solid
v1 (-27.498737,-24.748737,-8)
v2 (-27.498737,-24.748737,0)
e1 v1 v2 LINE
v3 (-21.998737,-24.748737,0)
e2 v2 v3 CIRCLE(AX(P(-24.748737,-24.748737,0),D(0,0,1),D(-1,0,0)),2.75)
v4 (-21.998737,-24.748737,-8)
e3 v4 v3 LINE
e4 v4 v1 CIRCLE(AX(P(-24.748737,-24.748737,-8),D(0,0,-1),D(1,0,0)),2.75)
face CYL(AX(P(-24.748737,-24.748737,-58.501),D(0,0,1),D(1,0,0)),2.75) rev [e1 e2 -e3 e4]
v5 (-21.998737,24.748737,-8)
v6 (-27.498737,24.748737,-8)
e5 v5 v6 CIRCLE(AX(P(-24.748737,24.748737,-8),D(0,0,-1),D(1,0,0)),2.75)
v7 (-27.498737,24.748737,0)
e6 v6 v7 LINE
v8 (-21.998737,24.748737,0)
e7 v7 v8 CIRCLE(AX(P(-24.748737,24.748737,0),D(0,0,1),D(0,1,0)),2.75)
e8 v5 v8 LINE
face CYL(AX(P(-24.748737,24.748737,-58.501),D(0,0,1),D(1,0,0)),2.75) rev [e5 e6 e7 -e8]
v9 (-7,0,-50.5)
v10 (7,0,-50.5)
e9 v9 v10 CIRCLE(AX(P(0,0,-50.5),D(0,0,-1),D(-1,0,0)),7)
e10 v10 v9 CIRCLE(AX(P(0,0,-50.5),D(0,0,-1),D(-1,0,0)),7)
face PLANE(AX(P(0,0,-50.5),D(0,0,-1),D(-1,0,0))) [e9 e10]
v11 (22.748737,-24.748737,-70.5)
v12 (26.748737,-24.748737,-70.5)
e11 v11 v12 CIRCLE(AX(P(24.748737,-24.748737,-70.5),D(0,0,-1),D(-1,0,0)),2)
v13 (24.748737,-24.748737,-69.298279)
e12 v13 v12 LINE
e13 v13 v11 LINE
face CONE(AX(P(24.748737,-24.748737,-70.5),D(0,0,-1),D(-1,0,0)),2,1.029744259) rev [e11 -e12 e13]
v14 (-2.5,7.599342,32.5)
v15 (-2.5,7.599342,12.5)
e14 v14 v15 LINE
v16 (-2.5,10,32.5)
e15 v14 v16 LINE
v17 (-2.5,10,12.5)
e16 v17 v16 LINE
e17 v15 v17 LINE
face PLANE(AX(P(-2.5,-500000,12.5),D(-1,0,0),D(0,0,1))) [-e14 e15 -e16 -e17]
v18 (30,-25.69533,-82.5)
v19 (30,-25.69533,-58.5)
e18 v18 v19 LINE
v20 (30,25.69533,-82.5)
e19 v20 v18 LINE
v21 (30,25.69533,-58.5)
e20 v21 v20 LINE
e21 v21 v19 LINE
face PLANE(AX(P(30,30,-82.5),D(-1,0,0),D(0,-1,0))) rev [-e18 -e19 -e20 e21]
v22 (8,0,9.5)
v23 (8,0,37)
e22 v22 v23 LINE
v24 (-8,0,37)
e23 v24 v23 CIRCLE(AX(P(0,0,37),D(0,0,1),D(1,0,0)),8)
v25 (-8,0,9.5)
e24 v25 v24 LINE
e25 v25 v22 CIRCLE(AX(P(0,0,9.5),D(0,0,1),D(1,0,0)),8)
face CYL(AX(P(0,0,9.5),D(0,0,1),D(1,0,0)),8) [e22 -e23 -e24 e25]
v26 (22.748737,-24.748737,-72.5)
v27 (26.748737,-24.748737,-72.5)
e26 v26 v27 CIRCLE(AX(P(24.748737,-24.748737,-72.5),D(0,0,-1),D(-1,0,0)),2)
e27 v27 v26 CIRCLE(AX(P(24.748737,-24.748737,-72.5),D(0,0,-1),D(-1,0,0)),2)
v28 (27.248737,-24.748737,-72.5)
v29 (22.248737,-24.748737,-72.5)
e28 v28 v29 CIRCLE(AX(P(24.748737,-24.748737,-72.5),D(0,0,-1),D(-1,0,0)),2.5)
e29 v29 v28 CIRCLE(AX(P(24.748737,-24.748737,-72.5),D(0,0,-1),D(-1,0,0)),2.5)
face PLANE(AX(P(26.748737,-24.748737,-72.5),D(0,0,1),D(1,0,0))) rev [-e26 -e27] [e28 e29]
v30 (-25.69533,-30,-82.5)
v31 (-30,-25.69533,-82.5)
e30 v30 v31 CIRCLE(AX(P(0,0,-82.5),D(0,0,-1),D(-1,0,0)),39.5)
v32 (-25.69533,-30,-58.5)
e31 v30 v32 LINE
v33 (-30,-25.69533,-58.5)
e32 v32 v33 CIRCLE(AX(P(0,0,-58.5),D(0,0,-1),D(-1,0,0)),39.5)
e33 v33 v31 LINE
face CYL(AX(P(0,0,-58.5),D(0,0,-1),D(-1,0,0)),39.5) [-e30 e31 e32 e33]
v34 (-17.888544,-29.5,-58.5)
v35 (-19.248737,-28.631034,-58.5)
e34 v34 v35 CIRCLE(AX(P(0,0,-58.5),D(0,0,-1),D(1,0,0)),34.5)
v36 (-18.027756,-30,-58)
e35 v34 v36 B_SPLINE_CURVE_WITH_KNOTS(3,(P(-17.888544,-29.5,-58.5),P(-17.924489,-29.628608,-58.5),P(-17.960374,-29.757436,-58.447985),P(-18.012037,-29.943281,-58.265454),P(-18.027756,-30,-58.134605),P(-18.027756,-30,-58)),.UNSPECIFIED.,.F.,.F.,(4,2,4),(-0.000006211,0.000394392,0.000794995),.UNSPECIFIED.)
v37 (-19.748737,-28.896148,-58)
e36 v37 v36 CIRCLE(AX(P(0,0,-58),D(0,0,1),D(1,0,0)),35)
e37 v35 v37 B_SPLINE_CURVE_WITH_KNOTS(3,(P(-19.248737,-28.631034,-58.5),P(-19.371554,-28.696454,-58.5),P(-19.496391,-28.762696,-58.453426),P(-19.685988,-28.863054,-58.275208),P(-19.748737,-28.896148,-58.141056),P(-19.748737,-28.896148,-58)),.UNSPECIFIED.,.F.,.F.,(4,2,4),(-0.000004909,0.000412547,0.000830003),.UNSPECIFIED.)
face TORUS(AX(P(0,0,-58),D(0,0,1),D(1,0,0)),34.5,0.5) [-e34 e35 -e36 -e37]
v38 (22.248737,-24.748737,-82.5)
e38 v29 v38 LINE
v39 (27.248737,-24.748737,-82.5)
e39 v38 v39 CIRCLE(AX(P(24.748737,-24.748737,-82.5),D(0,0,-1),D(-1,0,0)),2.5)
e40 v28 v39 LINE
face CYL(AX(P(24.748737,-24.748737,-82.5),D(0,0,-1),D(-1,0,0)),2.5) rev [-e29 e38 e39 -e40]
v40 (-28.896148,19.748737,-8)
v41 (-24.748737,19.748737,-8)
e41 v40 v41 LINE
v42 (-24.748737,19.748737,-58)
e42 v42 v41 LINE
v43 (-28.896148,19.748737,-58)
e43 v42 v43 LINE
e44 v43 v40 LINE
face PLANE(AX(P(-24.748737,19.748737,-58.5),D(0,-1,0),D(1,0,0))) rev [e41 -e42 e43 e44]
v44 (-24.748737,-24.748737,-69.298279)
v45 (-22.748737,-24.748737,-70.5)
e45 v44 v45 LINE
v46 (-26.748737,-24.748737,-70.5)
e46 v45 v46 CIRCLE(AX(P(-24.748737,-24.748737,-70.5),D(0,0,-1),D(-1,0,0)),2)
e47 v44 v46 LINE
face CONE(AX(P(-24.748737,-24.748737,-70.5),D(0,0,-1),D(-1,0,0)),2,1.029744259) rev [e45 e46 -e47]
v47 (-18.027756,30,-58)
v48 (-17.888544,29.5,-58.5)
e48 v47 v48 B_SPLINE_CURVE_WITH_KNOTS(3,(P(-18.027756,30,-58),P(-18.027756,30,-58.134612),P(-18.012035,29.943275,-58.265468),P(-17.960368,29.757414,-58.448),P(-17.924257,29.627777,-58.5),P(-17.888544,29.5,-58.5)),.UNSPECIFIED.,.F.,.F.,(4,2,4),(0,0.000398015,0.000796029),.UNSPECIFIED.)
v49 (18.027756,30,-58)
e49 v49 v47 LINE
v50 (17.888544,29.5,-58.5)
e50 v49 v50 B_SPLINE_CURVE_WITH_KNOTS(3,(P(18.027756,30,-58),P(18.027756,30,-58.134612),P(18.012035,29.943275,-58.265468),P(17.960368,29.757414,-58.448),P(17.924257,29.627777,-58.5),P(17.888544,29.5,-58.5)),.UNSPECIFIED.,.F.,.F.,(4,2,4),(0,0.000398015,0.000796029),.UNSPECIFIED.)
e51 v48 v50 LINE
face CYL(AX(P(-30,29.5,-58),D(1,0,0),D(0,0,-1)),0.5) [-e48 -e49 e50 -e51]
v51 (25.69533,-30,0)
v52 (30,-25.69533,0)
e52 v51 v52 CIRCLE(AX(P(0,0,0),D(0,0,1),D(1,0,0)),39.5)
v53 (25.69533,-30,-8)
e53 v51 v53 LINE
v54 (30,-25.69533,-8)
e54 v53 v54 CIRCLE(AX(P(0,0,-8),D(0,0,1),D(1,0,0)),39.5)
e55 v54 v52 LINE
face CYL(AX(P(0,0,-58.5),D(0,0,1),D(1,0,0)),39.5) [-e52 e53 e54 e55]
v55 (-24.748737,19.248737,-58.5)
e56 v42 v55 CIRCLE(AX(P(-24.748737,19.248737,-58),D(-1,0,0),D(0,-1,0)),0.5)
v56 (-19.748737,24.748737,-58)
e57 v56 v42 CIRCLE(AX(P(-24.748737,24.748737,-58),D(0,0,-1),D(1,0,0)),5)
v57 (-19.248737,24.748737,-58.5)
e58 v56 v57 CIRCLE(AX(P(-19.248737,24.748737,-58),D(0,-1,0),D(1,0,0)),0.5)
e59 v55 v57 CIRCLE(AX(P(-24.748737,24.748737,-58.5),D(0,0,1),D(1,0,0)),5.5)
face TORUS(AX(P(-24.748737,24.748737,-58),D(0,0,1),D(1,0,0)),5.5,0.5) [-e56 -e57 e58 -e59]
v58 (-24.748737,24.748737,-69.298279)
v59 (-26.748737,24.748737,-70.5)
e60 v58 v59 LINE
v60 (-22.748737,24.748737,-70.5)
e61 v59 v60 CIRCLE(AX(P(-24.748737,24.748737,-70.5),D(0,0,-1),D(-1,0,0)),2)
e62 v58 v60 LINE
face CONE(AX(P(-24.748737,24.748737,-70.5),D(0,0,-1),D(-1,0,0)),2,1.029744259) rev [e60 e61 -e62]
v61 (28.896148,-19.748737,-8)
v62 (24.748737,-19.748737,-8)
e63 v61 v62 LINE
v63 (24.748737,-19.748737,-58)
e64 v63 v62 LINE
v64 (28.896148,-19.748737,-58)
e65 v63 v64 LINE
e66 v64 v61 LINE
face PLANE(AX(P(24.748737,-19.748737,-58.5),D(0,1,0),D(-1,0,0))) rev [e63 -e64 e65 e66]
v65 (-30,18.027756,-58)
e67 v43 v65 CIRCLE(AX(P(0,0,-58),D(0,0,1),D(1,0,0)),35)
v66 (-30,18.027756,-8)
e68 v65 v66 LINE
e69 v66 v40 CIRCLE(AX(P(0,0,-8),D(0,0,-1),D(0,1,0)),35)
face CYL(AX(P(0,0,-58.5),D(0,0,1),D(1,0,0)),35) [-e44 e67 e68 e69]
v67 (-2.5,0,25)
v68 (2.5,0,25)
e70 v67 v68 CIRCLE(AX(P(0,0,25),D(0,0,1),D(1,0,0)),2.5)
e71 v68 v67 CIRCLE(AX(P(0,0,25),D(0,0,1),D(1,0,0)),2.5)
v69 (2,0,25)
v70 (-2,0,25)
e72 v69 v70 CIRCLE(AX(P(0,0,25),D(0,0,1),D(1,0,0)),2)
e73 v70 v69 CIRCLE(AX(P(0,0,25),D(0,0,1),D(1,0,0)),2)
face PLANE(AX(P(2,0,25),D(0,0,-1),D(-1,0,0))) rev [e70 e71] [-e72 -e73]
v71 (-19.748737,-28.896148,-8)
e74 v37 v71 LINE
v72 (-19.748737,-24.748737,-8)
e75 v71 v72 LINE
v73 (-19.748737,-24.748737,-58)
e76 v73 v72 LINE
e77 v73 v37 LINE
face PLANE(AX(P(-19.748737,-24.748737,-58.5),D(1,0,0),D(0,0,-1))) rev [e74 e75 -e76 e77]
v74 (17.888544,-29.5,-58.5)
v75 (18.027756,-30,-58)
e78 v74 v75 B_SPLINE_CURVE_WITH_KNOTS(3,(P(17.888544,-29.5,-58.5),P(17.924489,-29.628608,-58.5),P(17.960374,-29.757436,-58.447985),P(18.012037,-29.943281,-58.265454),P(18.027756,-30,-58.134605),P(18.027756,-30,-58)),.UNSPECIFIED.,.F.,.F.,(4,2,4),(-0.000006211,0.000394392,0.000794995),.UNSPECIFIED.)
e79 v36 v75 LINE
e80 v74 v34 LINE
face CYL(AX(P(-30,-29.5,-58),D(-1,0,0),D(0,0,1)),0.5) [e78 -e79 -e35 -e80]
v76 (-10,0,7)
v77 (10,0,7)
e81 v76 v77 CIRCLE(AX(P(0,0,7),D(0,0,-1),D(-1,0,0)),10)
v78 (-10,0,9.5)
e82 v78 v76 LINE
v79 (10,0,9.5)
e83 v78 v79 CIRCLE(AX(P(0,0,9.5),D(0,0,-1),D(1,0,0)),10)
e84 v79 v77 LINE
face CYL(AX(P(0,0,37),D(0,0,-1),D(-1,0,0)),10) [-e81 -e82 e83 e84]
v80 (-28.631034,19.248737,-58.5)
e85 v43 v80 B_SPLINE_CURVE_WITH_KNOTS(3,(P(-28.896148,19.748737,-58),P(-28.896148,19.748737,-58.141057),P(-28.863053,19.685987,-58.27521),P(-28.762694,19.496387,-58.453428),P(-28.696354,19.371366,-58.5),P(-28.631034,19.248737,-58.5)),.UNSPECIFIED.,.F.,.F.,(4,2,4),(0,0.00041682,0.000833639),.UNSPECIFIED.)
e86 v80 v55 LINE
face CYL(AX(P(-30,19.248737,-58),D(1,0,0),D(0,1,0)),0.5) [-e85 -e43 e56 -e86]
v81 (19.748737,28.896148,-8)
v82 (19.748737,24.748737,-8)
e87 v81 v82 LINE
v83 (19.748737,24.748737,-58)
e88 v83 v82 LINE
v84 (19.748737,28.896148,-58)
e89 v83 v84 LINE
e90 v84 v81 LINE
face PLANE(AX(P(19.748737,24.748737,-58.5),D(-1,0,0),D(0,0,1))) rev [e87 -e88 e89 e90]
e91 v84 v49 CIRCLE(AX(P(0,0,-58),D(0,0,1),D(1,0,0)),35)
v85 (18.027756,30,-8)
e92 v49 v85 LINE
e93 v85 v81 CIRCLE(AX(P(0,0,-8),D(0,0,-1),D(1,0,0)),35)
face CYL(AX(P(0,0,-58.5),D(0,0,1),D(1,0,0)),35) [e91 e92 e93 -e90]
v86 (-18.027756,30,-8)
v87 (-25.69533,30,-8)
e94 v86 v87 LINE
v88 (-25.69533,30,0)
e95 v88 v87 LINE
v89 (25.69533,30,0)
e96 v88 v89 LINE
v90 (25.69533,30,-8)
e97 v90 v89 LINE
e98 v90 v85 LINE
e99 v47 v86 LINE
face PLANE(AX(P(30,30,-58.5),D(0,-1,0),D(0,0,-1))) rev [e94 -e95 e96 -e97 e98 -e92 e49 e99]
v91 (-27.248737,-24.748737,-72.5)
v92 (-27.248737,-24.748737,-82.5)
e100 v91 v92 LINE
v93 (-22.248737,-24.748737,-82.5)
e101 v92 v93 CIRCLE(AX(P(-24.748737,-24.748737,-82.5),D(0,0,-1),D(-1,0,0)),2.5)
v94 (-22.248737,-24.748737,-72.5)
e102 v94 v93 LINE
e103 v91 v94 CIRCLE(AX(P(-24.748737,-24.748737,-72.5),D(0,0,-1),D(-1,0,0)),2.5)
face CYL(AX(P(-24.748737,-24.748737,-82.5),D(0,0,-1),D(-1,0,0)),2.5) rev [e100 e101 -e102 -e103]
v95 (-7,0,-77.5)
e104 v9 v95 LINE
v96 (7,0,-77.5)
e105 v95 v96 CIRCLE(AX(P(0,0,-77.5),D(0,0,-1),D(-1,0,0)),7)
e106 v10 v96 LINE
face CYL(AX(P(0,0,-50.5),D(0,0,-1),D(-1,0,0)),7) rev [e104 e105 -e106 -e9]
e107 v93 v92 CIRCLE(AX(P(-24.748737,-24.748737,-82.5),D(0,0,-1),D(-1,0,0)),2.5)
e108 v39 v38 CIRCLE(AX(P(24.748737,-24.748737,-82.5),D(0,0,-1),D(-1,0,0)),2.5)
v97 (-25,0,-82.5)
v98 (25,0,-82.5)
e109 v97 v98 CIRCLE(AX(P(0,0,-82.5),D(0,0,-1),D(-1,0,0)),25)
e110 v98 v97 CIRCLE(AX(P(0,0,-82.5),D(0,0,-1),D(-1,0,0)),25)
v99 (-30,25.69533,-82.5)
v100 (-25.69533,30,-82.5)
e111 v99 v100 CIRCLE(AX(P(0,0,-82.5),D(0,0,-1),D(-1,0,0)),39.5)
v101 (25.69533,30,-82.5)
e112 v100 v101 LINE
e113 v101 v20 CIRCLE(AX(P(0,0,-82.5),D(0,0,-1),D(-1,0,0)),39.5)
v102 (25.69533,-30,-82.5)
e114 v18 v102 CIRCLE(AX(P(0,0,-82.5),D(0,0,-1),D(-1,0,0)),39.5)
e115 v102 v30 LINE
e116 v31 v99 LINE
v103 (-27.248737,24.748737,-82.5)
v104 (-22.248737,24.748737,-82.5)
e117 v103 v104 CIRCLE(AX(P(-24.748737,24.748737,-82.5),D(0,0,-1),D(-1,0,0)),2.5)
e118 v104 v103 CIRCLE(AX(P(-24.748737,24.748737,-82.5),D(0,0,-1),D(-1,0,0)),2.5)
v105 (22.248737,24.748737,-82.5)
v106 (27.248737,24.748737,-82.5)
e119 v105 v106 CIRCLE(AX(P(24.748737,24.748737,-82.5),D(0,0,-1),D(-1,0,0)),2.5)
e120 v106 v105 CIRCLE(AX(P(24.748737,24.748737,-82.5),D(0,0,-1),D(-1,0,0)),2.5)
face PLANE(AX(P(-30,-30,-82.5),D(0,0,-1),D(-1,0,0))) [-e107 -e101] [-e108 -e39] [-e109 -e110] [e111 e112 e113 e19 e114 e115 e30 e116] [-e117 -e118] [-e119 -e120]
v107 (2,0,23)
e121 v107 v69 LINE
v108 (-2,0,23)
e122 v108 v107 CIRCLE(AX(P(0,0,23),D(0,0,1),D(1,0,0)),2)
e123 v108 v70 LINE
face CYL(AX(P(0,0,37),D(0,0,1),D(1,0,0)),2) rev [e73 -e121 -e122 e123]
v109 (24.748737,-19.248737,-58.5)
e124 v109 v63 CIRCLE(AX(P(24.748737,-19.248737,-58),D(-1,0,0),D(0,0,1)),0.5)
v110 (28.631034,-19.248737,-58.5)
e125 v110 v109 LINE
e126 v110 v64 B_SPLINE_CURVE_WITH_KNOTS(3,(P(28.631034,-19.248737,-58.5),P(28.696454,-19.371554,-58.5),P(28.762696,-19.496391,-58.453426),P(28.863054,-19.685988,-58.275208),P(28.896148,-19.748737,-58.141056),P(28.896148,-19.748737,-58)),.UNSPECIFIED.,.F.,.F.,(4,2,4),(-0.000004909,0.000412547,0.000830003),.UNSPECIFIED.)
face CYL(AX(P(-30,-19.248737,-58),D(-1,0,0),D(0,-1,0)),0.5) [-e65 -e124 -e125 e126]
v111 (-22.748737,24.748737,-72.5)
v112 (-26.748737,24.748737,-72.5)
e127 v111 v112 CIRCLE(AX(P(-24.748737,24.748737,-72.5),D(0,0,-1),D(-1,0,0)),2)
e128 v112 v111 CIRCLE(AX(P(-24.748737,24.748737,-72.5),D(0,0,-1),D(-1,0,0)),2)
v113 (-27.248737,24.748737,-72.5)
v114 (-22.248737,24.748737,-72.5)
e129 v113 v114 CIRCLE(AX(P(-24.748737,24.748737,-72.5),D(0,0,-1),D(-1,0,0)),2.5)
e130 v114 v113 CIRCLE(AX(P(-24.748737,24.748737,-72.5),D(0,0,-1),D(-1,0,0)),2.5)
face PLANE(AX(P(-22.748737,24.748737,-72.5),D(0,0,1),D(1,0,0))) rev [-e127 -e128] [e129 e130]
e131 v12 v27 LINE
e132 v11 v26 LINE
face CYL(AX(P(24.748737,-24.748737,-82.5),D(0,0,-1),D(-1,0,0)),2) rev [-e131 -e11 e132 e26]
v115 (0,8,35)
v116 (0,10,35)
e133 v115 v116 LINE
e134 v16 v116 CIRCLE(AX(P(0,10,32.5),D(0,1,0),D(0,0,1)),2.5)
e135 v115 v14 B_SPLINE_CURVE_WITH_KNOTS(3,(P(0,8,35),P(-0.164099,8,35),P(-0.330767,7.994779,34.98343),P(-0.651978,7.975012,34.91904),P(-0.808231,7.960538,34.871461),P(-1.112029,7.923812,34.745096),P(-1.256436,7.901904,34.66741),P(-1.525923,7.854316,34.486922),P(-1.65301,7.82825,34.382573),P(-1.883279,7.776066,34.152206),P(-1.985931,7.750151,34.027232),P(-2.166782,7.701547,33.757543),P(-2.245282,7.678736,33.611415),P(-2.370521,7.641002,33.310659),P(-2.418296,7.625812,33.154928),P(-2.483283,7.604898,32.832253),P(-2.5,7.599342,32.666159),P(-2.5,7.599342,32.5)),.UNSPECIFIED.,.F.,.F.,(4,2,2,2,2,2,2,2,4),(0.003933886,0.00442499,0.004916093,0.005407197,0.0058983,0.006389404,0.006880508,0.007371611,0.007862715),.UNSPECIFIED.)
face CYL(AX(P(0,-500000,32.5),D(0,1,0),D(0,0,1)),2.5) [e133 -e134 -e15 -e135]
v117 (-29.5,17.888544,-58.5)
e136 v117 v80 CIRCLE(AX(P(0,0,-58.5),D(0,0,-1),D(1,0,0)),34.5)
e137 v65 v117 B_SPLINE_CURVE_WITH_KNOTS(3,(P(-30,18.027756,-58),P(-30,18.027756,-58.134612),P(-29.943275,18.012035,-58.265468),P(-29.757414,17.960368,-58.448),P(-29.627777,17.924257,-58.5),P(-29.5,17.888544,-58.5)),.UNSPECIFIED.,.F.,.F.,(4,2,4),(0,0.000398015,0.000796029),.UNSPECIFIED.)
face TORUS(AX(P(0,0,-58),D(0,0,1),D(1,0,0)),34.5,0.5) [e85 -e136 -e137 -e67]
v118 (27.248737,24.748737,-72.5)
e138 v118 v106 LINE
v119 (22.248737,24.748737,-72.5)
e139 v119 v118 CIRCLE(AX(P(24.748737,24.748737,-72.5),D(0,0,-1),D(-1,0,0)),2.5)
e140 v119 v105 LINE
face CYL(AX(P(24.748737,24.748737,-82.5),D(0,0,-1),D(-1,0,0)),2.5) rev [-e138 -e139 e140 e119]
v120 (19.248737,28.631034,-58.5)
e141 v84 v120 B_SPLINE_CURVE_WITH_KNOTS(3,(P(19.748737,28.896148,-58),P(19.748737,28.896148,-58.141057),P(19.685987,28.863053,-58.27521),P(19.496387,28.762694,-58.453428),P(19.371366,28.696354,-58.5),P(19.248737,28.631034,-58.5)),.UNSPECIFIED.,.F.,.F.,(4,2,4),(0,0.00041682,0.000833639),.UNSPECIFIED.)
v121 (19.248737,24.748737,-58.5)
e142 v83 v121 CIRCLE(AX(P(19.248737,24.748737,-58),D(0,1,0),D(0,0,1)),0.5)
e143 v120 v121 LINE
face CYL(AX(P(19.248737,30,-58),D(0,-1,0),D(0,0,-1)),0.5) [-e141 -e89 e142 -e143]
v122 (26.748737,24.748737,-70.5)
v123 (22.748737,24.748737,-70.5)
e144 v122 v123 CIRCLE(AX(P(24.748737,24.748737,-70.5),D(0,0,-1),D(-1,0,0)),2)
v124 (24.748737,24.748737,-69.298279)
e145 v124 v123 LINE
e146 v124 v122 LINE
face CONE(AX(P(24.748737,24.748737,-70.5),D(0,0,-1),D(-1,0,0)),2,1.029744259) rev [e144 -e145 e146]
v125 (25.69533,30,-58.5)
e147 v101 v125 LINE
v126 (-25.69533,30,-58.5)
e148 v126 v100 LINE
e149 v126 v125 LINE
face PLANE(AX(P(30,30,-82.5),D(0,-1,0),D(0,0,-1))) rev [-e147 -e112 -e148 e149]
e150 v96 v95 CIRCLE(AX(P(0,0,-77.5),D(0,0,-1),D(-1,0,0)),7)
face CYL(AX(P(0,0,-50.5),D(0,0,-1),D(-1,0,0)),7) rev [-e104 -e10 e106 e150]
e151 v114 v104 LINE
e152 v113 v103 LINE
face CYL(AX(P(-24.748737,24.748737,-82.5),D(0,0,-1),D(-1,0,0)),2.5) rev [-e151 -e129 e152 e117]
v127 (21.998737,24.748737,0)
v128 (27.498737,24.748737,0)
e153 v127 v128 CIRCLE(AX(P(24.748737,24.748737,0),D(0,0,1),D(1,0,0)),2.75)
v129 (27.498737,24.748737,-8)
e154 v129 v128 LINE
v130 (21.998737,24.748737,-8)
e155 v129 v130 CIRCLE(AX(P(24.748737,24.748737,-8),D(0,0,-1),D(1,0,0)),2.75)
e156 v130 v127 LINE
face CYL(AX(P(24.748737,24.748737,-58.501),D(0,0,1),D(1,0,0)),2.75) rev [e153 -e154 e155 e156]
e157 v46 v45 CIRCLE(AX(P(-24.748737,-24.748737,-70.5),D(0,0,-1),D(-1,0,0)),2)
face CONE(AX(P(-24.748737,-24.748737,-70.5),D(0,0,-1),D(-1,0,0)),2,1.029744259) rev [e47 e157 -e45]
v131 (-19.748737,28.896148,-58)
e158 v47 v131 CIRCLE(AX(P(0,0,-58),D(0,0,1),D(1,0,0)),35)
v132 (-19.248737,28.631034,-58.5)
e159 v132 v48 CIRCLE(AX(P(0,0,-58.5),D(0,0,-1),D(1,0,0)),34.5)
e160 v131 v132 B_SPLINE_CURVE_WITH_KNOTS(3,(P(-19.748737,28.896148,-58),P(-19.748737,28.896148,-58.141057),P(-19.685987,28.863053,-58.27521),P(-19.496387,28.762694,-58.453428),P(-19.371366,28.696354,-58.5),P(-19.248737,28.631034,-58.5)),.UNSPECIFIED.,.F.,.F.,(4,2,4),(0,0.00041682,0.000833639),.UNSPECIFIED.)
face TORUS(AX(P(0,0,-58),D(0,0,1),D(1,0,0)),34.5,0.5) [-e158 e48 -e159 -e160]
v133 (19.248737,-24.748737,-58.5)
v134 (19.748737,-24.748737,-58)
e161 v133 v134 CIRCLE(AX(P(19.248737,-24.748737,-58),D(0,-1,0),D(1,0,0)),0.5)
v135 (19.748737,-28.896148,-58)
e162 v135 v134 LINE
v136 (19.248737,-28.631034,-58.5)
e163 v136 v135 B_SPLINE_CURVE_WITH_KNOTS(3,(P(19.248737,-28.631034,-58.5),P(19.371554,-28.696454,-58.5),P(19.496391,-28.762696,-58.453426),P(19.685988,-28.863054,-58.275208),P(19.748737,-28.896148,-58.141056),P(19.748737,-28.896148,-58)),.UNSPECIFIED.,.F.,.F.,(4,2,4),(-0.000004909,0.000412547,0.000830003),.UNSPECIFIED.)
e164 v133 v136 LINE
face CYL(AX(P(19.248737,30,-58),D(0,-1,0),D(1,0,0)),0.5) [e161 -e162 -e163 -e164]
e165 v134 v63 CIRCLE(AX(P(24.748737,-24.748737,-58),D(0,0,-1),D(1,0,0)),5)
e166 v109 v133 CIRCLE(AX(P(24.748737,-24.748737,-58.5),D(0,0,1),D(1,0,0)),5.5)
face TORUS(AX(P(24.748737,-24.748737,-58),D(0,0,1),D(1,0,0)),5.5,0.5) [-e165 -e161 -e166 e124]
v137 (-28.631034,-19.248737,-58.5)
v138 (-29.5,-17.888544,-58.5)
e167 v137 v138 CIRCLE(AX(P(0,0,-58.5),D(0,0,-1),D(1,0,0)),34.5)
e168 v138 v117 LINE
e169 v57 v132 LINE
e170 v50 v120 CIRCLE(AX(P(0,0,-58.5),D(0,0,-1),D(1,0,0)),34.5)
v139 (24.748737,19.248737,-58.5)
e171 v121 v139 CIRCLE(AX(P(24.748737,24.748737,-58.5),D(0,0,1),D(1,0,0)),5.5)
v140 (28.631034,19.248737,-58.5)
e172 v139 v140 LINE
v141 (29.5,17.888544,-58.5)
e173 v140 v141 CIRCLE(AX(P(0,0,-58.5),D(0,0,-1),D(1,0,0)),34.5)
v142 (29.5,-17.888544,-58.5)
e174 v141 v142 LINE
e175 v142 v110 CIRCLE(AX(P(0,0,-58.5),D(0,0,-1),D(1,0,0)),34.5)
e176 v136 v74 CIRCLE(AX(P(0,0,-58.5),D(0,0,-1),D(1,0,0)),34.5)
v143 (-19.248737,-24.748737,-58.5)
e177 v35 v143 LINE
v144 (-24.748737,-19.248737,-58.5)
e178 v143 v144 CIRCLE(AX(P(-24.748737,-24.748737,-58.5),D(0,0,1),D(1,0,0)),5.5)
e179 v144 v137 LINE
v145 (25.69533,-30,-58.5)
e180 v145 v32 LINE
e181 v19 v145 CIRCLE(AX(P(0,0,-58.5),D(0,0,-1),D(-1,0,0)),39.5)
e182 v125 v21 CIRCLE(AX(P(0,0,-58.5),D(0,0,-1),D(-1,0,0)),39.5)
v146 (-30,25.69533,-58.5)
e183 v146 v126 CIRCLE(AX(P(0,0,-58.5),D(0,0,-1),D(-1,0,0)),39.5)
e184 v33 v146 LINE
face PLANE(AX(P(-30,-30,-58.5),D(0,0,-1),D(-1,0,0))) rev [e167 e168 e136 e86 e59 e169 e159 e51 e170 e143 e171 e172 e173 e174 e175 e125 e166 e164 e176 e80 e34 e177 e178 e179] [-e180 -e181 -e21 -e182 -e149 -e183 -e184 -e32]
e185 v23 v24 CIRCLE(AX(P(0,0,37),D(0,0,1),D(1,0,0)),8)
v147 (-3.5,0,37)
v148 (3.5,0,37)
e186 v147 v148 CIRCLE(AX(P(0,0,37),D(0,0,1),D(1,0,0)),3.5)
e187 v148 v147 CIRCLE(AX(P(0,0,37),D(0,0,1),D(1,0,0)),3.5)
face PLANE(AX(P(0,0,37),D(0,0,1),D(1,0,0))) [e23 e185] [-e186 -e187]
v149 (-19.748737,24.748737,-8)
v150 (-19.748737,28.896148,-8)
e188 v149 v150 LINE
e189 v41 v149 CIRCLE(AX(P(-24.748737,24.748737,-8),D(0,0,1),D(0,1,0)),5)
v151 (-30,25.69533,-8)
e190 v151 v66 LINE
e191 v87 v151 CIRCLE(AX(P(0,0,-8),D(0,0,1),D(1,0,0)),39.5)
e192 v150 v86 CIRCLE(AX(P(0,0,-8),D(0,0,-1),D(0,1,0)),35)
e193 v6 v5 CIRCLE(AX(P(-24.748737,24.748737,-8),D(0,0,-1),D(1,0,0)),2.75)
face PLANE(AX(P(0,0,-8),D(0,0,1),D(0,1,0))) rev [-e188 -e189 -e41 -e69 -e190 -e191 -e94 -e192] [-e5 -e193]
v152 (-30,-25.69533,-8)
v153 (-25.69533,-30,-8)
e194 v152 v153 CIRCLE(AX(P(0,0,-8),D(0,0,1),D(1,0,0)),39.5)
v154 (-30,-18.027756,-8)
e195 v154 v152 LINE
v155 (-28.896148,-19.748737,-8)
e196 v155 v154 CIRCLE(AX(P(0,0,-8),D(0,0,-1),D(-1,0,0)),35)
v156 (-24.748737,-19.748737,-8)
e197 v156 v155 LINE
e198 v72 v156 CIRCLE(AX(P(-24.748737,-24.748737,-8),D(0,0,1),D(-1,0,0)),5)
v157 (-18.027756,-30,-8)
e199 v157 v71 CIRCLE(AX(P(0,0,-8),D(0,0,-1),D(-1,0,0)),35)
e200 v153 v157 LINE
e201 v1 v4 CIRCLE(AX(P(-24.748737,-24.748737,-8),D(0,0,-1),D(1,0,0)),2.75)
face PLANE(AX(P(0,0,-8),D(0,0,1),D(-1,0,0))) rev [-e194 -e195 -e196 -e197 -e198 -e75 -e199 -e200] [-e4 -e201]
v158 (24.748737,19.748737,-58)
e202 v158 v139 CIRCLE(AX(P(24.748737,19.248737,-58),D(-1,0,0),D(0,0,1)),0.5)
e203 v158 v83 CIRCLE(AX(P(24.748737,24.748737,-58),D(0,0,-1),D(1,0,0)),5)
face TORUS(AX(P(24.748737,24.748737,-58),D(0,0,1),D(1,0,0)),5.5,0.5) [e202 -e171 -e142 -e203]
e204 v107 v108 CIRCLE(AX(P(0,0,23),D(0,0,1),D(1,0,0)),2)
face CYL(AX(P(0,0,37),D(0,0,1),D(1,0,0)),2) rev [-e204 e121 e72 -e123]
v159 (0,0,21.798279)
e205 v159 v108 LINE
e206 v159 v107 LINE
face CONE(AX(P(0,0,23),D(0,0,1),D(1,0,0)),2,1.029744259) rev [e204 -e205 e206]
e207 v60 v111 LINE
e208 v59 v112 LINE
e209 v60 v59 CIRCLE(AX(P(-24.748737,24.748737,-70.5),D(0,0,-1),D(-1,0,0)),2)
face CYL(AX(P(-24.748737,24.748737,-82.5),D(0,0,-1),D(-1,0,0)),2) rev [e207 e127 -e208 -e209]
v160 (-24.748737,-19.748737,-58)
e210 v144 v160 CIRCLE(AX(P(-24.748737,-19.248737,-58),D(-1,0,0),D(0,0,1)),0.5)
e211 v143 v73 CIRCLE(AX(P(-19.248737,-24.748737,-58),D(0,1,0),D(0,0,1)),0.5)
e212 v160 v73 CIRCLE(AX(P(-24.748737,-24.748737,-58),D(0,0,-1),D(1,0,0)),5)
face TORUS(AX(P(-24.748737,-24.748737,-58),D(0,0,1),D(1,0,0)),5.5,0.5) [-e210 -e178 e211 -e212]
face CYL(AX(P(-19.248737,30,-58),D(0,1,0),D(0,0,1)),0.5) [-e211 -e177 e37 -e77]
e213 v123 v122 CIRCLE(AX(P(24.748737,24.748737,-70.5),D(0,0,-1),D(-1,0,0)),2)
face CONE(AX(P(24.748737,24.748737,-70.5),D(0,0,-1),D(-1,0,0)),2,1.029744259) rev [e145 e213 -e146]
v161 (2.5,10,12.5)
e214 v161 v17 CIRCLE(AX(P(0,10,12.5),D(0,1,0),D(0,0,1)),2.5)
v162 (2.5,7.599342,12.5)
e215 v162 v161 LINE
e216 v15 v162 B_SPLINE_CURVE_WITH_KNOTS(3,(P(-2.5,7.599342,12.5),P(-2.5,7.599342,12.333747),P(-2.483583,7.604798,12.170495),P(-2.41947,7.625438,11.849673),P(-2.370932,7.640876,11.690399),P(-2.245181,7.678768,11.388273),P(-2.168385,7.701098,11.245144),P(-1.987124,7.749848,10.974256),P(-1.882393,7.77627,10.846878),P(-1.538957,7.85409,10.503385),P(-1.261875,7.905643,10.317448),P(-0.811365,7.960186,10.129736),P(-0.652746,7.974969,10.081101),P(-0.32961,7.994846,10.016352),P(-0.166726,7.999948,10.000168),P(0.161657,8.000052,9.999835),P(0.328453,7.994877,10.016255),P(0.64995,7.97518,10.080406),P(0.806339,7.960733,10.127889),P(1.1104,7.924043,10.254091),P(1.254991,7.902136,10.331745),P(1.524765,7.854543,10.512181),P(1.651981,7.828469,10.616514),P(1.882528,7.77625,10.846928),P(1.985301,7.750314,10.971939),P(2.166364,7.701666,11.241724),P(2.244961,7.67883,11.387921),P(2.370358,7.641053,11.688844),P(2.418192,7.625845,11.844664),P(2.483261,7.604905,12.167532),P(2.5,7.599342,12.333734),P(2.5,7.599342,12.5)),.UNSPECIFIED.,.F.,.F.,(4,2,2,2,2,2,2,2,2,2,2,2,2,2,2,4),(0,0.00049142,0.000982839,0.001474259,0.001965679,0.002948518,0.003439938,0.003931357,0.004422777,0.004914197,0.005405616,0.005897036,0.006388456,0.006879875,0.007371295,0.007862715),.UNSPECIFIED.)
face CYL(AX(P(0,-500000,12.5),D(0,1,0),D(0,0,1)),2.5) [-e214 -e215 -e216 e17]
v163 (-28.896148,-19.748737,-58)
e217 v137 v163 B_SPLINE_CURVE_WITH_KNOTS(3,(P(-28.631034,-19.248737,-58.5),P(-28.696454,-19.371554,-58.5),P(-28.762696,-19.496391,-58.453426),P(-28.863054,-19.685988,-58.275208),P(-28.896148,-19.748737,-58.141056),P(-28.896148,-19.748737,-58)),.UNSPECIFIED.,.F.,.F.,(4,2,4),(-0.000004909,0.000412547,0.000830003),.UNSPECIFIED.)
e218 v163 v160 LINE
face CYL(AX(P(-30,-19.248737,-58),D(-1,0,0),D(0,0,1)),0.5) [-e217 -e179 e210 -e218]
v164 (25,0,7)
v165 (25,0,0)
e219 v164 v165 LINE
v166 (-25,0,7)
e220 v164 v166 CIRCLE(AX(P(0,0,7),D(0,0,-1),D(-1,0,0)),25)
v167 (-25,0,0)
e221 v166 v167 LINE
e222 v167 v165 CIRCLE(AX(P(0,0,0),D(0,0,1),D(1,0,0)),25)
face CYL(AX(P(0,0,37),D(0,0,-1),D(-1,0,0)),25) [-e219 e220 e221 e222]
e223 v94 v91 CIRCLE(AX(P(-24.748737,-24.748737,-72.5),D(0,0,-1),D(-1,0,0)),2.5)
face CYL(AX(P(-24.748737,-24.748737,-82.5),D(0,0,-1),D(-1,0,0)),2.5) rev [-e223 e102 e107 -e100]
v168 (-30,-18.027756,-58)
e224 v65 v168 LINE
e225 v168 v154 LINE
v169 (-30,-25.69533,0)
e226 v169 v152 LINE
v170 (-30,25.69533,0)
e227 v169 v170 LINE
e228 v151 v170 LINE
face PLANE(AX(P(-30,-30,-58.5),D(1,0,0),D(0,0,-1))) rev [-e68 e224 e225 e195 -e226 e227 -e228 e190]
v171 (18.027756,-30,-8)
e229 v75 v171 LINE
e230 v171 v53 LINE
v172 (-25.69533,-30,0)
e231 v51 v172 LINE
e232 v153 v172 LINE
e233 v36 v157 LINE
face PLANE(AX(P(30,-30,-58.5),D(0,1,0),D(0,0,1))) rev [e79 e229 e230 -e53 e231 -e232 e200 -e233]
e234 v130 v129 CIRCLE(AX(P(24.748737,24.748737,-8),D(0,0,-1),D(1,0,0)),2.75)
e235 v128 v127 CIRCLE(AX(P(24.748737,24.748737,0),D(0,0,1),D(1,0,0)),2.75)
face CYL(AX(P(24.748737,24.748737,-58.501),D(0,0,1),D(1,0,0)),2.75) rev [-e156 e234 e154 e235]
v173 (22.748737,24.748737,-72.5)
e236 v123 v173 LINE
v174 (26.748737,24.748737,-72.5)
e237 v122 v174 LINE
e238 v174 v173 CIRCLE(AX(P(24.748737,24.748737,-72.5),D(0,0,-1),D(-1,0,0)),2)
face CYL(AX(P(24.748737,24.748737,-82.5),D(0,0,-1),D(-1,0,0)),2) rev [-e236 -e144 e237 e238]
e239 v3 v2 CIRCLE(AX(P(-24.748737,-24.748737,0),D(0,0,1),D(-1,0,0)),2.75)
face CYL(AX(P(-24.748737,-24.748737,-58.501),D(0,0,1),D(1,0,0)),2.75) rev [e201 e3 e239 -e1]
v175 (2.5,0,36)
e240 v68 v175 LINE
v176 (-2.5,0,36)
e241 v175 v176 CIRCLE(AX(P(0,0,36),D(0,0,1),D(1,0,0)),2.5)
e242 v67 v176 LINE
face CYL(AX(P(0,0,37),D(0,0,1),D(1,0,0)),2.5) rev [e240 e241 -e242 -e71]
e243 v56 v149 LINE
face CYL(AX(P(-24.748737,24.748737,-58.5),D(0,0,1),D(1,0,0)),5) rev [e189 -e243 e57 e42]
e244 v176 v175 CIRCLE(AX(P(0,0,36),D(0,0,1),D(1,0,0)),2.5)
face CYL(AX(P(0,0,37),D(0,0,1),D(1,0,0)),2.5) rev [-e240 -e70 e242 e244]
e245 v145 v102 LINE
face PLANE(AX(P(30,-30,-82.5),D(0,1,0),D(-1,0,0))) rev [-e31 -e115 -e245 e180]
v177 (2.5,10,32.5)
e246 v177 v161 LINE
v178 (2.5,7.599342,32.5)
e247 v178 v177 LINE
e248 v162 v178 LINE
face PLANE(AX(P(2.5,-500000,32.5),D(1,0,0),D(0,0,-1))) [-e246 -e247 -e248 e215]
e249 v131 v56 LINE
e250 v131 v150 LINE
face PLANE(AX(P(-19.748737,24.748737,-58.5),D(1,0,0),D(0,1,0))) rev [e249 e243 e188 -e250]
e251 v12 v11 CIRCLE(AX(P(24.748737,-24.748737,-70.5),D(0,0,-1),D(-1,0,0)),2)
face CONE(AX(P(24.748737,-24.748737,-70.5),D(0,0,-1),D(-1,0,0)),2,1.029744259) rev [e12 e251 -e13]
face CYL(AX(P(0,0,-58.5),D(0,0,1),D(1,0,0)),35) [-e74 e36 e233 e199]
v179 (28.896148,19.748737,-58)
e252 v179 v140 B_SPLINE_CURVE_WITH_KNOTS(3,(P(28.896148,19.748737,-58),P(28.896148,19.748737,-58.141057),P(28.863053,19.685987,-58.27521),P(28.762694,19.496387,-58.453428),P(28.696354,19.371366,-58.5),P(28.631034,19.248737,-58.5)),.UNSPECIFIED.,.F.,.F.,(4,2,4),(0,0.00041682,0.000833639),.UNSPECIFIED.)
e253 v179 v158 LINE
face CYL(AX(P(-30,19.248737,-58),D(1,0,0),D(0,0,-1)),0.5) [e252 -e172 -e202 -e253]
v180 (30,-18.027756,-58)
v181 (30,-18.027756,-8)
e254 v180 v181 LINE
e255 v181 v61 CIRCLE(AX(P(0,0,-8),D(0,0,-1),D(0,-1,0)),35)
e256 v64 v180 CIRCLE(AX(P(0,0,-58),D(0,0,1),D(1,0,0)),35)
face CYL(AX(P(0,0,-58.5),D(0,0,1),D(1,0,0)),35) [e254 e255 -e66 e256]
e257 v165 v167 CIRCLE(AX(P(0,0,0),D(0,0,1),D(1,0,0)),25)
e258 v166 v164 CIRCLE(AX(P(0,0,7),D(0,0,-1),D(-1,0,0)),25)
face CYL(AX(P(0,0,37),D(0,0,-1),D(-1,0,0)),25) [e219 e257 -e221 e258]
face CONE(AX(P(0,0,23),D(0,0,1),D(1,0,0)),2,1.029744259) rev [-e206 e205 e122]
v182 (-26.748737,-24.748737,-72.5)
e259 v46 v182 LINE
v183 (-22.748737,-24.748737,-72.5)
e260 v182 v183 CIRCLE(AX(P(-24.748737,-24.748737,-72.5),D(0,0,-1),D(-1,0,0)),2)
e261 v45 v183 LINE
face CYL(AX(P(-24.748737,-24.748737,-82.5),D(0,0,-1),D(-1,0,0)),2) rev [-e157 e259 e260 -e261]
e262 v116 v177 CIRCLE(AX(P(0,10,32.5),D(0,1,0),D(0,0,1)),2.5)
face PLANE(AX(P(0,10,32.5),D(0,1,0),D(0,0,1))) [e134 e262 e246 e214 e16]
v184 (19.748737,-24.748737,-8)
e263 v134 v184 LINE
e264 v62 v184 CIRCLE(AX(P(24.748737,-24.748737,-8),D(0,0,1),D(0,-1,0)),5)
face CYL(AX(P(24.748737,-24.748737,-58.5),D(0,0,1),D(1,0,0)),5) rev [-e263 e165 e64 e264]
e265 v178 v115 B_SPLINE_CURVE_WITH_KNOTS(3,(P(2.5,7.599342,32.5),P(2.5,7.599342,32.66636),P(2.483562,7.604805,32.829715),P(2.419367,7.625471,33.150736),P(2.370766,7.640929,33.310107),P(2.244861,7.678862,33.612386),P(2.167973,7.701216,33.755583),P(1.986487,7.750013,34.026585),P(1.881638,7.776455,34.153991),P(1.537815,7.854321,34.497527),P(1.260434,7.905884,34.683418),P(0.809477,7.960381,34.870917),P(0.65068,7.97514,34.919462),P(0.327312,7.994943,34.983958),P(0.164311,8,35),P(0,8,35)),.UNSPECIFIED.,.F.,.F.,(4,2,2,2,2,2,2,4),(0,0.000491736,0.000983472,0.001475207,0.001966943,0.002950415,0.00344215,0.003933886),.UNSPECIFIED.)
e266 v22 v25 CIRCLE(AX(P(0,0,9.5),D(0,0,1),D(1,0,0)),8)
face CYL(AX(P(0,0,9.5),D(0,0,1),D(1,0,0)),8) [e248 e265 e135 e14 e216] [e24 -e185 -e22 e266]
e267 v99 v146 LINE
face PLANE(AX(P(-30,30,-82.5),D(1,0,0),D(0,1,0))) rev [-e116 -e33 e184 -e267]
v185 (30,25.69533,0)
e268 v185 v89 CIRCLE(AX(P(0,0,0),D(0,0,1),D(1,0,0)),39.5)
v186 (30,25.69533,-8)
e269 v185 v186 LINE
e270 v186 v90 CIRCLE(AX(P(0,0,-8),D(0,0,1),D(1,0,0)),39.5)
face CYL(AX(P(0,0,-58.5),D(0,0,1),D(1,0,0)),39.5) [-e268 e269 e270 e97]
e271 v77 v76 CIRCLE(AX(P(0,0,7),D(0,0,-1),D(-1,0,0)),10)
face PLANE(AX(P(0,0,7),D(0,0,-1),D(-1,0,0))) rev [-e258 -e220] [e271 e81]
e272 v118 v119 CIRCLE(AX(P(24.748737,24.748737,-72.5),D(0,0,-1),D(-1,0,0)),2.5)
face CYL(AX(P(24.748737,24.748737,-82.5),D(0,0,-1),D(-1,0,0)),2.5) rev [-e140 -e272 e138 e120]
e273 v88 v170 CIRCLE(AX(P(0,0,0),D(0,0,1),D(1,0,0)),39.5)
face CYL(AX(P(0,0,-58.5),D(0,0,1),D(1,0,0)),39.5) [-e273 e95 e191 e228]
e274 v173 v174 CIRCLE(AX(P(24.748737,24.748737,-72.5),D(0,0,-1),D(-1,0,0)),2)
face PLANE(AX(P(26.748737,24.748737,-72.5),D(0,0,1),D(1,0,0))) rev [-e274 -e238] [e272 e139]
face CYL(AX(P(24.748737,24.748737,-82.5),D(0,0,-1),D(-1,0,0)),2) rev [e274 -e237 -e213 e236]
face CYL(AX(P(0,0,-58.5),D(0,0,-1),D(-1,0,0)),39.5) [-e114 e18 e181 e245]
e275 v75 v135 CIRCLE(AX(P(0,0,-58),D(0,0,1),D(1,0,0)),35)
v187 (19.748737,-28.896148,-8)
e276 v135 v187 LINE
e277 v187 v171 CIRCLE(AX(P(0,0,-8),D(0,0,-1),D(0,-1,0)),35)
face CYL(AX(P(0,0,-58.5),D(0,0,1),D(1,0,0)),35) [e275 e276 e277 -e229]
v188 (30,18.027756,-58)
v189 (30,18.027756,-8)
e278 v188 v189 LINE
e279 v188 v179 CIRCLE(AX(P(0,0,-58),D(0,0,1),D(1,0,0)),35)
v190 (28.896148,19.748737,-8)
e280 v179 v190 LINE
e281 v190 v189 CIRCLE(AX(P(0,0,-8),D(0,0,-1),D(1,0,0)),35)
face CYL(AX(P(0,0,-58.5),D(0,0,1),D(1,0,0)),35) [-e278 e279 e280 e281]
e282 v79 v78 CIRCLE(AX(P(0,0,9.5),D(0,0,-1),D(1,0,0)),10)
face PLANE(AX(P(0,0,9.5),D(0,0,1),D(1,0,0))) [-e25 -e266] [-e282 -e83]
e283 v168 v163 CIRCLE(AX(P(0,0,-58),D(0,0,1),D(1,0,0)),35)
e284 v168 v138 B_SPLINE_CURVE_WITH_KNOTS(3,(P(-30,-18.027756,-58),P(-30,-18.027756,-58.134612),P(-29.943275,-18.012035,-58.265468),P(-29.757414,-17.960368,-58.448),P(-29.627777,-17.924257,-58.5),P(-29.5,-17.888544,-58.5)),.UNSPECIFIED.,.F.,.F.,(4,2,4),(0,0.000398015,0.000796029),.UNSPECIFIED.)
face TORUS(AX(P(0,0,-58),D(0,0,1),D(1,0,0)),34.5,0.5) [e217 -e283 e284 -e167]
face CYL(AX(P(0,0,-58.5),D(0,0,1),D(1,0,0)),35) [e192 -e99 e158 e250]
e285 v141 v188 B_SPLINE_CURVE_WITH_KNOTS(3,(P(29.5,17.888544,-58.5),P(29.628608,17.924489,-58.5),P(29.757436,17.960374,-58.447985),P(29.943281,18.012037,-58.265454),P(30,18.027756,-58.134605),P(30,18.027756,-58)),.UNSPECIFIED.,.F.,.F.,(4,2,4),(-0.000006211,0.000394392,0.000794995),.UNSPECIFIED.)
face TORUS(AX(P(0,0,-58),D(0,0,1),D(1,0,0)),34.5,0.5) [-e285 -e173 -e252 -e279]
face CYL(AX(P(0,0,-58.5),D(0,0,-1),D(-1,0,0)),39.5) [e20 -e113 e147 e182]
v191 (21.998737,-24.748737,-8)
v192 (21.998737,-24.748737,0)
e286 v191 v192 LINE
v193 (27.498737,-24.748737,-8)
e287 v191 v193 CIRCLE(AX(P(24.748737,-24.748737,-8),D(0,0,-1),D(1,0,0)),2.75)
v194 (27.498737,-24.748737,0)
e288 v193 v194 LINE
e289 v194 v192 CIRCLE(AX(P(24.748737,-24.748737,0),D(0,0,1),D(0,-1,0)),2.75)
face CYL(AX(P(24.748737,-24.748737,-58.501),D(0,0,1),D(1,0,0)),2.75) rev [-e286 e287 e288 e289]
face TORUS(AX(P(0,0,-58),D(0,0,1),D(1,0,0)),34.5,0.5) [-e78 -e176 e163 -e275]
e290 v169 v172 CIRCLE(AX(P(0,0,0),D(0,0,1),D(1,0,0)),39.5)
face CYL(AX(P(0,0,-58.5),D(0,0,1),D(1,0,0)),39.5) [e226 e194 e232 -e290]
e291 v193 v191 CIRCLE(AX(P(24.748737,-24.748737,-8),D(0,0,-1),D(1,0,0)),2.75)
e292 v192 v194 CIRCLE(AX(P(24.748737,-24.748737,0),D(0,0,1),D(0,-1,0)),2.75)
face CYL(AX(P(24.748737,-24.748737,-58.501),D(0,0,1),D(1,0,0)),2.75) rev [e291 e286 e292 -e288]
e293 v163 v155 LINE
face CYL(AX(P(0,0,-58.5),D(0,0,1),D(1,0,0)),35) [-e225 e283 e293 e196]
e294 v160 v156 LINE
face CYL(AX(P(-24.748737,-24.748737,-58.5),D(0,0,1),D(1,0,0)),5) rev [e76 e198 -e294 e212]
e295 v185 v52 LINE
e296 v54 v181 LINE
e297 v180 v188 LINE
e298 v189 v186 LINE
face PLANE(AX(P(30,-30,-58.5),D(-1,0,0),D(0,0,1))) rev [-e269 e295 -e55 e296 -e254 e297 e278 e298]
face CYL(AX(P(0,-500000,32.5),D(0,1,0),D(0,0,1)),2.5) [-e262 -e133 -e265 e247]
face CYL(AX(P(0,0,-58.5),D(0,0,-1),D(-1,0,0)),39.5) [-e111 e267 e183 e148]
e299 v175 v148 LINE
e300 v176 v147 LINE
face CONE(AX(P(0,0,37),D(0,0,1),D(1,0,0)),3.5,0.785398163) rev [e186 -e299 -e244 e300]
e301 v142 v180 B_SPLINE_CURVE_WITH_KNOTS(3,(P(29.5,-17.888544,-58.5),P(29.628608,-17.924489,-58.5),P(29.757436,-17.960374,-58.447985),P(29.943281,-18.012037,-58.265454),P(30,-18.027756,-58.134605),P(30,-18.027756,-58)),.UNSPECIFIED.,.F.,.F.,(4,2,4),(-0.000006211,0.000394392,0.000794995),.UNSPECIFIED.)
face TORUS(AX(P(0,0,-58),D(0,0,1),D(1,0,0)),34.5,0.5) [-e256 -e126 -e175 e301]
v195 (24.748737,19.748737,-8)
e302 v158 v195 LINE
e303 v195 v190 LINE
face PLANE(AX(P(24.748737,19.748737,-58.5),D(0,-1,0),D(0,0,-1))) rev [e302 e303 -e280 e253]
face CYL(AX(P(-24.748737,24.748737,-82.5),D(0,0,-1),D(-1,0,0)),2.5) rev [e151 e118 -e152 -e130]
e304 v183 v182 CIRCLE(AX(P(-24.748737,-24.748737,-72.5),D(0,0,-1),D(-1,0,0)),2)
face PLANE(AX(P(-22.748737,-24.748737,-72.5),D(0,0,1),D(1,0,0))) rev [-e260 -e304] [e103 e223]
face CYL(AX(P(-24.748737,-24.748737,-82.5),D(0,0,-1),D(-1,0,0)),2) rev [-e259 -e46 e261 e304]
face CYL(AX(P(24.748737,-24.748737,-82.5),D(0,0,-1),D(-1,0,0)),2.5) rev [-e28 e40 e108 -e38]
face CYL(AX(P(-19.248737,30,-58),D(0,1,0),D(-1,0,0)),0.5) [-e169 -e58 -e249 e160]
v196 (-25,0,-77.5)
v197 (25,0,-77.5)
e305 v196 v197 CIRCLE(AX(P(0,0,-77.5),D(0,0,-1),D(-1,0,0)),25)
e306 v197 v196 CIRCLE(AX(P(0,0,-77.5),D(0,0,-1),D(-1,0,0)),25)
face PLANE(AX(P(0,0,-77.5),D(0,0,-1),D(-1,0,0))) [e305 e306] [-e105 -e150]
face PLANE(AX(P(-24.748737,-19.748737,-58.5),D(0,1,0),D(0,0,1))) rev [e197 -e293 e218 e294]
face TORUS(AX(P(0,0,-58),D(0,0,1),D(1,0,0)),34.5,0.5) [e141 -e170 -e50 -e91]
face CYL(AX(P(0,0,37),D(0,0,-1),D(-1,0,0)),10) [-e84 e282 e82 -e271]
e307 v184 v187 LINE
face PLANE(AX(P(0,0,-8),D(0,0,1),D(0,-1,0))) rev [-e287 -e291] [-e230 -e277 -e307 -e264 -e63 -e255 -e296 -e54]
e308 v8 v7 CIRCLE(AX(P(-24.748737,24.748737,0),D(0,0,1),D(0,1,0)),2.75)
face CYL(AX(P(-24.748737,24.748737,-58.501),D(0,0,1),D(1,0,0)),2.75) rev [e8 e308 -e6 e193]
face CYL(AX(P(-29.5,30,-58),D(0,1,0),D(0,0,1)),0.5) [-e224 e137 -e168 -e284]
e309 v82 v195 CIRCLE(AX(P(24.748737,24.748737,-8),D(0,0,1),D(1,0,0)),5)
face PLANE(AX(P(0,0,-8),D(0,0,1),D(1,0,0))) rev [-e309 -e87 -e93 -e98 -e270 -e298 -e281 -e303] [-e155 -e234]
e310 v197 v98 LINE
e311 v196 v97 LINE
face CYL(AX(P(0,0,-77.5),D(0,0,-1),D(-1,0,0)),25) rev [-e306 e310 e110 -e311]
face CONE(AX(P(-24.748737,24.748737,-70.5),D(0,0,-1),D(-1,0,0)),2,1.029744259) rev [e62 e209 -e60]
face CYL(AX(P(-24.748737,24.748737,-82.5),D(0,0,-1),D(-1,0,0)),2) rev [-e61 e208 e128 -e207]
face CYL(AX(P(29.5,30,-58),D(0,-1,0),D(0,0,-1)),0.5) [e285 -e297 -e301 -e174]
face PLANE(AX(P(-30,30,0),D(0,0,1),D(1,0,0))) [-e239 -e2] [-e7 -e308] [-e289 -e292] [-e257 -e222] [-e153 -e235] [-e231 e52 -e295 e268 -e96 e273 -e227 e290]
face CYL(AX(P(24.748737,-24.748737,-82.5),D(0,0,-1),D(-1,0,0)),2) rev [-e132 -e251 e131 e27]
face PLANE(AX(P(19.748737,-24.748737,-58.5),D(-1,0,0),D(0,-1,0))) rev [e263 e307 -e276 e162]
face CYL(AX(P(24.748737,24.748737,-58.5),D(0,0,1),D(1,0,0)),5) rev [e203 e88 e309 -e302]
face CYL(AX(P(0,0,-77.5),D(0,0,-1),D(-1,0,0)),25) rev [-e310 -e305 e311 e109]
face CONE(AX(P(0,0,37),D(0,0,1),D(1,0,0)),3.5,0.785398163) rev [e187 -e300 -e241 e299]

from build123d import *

# Parameters (mm, degrees)
SKETCH_1_R               = 25
EXTRUDE_2137_DEPTH       = 37
SKETCH_2_OUTSIDE_W       = 67.962
SKETCH_2_OUTSIDE_H       = 67.962
SKETCH_2_OUTSIDE_R       = 10
CUT_EXTRUDE_1_DEPTH      = 47.368092477
SKETCH_3_OUTSIDE_W       = 67.962
SKETCH_3_OUTSIDE_H       = 67.962
SKETCH_3_OUTSIDE_R       = 8
CUT_EXTRUDE_2_DEPTH      = 27.5
EXTRUDE_2_REACH          = 58.736
EXTRUDE_2_END_RADIUS     = 8
SKETCH_6_W               = 60
SKETCH_6_H               = 60
EXTRUDE_2668_DEPTH       = 58.5
CUT_EXTRUDE_8_DEPTH      = 66.956425009
PATTERN_CIRCULAR_2_COUNT = 4
CUT_EXTRUDE_6_REACH      = 74.265
SKETCH_9_R               = 2.75
PATTERN_CIRCULAR_1_COUNT = 4
SKETCH_10_OUTSIDE_W      = 87.55
SKETCH_10_OUTSIDE_H      = 87.55
SKETCH_10_OUTSIDE_R      = 39.5
CUT_EXTRUDE_7_DEPTH      = 73.265136823
FILLET_3_R               = 0.5
SKETCH_15_W              = 60
SKETCH_15_H              = 60
EXTRUDE_8537_DEPTH       = 24
SKETCH_21_OUTSIDE_W      = 91.312
SKETCH_21_OUTSIDE_H      = 91.312
SKETCH_21_OUTSIDE_R      = 39.5
CUT_EXTRUDE_10_DEPTH     = 24
SKETCH_22_R              = 25
CUT_EXTRUDE_11_DEPTH     = 5
SKETCH_30_R              = 7
CUT_EXTRUDE_15_DEPTH     = 32
PATTERN_CIRCULAR_3_COUNT = 4


with BuildPart() as part:
    # 草图1 → Extrude 2137 (new body)
    with BuildSketch(Plane.XY):
        Circle(SKETCH_1_R)
    extrude(amount=EXTRUDE_2137_DEPTH)

    # 草图2 outside → 切除-拉伸1 (cut, through all)
    with BuildSketch(Plane(origin=(0, 0, 7), x_dir=(-1, 0, 0), z_dir=(0, 0, -1))):
        Rectangle(SKETCH_2_OUTSIDE_W, SKETCH_2_OUTSIDE_H)
        Circle(SKETCH_2_OUTSIDE_R, mode=Mode.SUBTRACT)
    extrude(amount=-CUT_EXTRUDE_1_DEPTH, mode=Mode.SUBTRACT)

    # 草图3 outside → 切除-拉伸2 (cut)
    with BuildSketch(Plane.XY.offset(37)):
        Rectangle(SKETCH_3_OUTSIDE_W, SKETCH_3_OUTSIDE_H)
        Circle(SKETCH_3_OUTSIDE_R, mode=Mode.SUBTRACT)
    extrude(amount=-CUT_EXTRUDE_2_DEPTH, mode=Mode.SUBTRACT)

    # 凸台-拉伸2: up to this cylinder (the profile starts outside it)
    extrude_2_end = Plane(origin=(0, 0, 22.5), z_dir=(0, 0, 1)) * Cylinder(EXTRUDE_2_END_RADIUS, 134.472, mode=Mode.PRIVATE)
    # 草图4 → 凸台-拉伸2 (add, up to the surface)
    with BuildSketch(Plane(origin=(0, 10, 0), x_dir=(-1, 0, 0), z_dir=(0, 1, 0)), mode=Mode.PRIVATE) as extrude_2_sk1:
        with BuildLine():
            Line((-2.5, 32.5), (-2.5, 12.5))
            ThreePointArc((-2.5, 12.5), (0, 10), (2.5, 12.5))
            Line((2.5, 12.5), (2.5, 32.5))
            ThreePointArc((2.5, 32.5), (0, 35), (-2.5, 32.5))
        make_face()
    extrude_2_tool1 = extrude(extrude_2_sk1.sketch, amount=-EXTRUDE_2_REACH, mode=Mode.PRIVATE) - extrude_2_end
    add(extrude_2_tool1.solids().sort_by_distance((0, 10, 22.5))[0])

    # 草图6 → Extrude 2668 (add)
    with BuildSketch(Plane(origin=(0, 0, 0), x_dir=(-1, 0, 0), z_dir=(0, 0, -1))):
        Rectangle(SKETCH_6_W, SKETCH_6_H)
    extrude(amount=EXTRUDE_2668_DEPTH)

    # 草图7 → 切除-拉伸8 (cut, through all)
    with BuildSketch(Plane.XY.offset(-8)):
        with BuildLine():
            Line((24.748737342, 19.748737342), (28.896148072, 19.748737342))
            ThreePointArc((28.896148072, 19.748737342), (29.460643379, 18.896308944), (30, 18.027756377))
            Line((30, 18.027756377), (30, 30))
            Line((30, 30), (18.027756377, 30))
            ThreePointArc((18.027756377, 30), (18.896308944, 29.460643379), (19.748737342, 28.896148072))
            Line((19.748737342, 28.896148072), (19.748737342, 24.748737342))
            ThreePointArc((19.748737342, 24.748737342), (21.213203436, 21.213203436), (24.748737342, 19.748737342))
        make_face()
    cut_extrude_8 = extrude(amount=-CUT_EXTRUDE_8_DEPTH, mode=Mode.SUBTRACT)

    # 阵列(圆周)2: 切除-拉伸8 ×4 about axis
    pattern_circular_2_axis = Axis((0, 0, 0), (0, 0, 1))
    for i in range(1, PATTERN_CIRCULAR_2_COUNT):
        add(cut_extrude_8.rotate(pattern_circular_2_axis, i * 360 / PATTERN_CIRCULAR_2_COUNT), mode=Mode.SUBTRACT)

    # 草图9 → 切除-拉伸6 (cut, up to next)
    with BuildSketch(Plane.XY, mode=Mode.PRIVATE) as cut_extrude_6_sk1:
        with Locations((24.748737342, 24.748737342)):
            Circle(SKETCH_9_R)
    cut_extrude_6_tool1 = extrude(cut_extrude_6_sk1.sketch, amount=-CUT_EXTRUDE_6_REACH, mode=Mode.PRIVATE) & part.part
    cut_extrude_6 = cut_extrude_6_tool1.solids().sort_by_distance((24.748737, 24.748737, 0))[0]
    add(cut_extrude_6, mode=Mode.SUBTRACT)

    # 阵列(圆周)1: 切除-拉伸6 ×4 about axis
    pattern_circular_1_axis = Axis((0, 0, 0), (0, 0, 1))
    for i in range(1, PATTERN_CIRCULAR_1_COUNT):
        add(cut_extrude_6.rotate(pattern_circular_1_axis, i * 360 / PATTERN_CIRCULAR_1_COUNT), mode=Mode.SUBTRACT)

    # 草图10 outside → 切除-拉伸7 (cut, through all)
    with BuildSketch(Plane.XY):
        Rectangle(SKETCH_10_OUTSIDE_W, SKETCH_10_OUTSIDE_H)
        Circle(SKETCH_10_OUTSIDE_R, mode=Mode.SUBTRACT)
    extrude(amount=-CUT_EXTRUDE_7_DEPTH, mode=Mode.SUBTRACT)

    # 圆角3
    fillet_3_edges = [part.edges().sort_by_distance(p)[0] for p in [
        (-30, 0, -58.5),
        (-18.896308944, -29.460643379, -58.5),
        (-29.460643379, -18.896308944, -58.5),
        (-26.822442707, -19.748737342, -58.5),
        (-21.213203436, -21.213203436, -58.5),
        (-19.748737342, -26.822442707, -58.5),
        (0, 30, -58.5),
        (-29.460643379, 18.896308944, -58.5),
        (-18.896308944, 29.460643379, -58.5),
        (-19.748737342, 26.822442707, -58.5),
        (-21.213203436, 21.213203436, -58.5),
        (-26.822442707, 19.748737342, -58.5),
        (30, 0, -58.5),
        (18.896308944, 29.460643379, -58.5),
        (29.460643379, 18.896308944, -58.5),
        (26.822442707, 19.748737342, -58.5),
        (21.213203436, 21.213203436, -58.5),
        (19.748737342, 26.822442707, -58.5),
        (0, -30, -58.5),
        (29.460643379, -18.896308944, -58.5),
        (18.896308944, -29.460643379, -58.5),
        (19.748737342, -26.822442707, -58.5),
        (21.213203436, -21.213203436, -58.5),
        (26.822442707, -19.748737342, -58.5),
    ]]
    fillet(fillet_3_edges, radius=FILLET_3_R)

    # 草图15 → Extrude 8537 (add)
    with BuildSketch(Plane(origin=(0, 0, -58.5), x_dir=(-1, 0, 0), z_dir=(0, 0, -1))):
        Rectangle(SKETCH_15_W, SKETCH_15_H)
    extrude(amount=EXTRUDE_8537_DEPTH)

    # 草图21 outside → 切除-拉伸10 (cut)
    with BuildSketch(Plane(origin=(0, 0, -82.5), x_dir=(-1, 0, 0), z_dir=(0, 0, -1))):
        Rectangle(SKETCH_21_OUTSIDE_W, SKETCH_21_OUTSIDE_H)
        Circle(SKETCH_21_OUTSIDE_R, mode=Mode.SUBTRACT)
    extrude(amount=-CUT_EXTRUDE_10_DEPTH, mode=Mode.SUBTRACT)

    # 草图22 → 切除-拉伸11 (cut)
    with BuildSketch(Plane(origin=(0, 0, -82.5), x_dir=(-1, 0, 0), z_dir=(0, 0, -1))):
        Circle(SKETCH_22_R)
    extrude(amount=-CUT_EXTRUDE_11_DEPTH, mode=Mode.SUBTRACT)

    # 草图30 → 切除-拉伸15 (cut)
    with BuildSketch(Plane(origin=(0, 0, -82.5), x_dir=(-1, 0, 0), z_dir=(0, 0, -1))):
        Circle(SKETCH_30_R)
    extrude(amount=-CUT_EXTRUDE_15_DEPTH, mode=Mode.SUBTRACT)

    # 草图31 → M5 螺纹孔1 (revolve, cut)
    with BuildSketch(Plane(origin=(0, 0, 37), x_dir=(0, -1, 0), z_dir=(1, 0, 0))):
        Polygon((0, 0), (0, 15.201721238), (2, 14), (2, 12), (2.5, 12), (2.5, 1), (3.5, 0), align=None)
    revolve(axis=Axis((0, 0, 43.35), (0, 0, -1)), mode=Mode.SUBTRACT)

    # 草图34 → M5 螺纹孔2 (revolve, cut)
    with BuildSketch(Plane(origin=(-24.748737342, 24.748737342, -82.5), x_dir=(0, 1, 0), z_dir=(1, 0, 0))):
        Polygon((0, 0), (0, 13.201721238), (2, 12), (2, 10), (2.5, 10), (2.5, 0), align=None)
    hole_wizard_m5_2 = revolve(axis=Axis((-24.748737342, 24.748737342, -88.85), (0, 0, 1)), mode=Mode.SUBTRACT)

    # 阵列(圆周)3: M5 螺纹孔2 ×4 about axis
    pattern_circular_3_axis = Axis((0, 0, 0), (0, 0, 1))
    for i in range(1, PATTERN_CIRCULAR_3_COUNT):
        add(hole_wizard_m5_2.rotate(pattern_circular_3_axis, i * 360 / PATTERN_CIRCULAR_3_COUNT), mode=Mode.SUBTRACT)


solid = part.part
